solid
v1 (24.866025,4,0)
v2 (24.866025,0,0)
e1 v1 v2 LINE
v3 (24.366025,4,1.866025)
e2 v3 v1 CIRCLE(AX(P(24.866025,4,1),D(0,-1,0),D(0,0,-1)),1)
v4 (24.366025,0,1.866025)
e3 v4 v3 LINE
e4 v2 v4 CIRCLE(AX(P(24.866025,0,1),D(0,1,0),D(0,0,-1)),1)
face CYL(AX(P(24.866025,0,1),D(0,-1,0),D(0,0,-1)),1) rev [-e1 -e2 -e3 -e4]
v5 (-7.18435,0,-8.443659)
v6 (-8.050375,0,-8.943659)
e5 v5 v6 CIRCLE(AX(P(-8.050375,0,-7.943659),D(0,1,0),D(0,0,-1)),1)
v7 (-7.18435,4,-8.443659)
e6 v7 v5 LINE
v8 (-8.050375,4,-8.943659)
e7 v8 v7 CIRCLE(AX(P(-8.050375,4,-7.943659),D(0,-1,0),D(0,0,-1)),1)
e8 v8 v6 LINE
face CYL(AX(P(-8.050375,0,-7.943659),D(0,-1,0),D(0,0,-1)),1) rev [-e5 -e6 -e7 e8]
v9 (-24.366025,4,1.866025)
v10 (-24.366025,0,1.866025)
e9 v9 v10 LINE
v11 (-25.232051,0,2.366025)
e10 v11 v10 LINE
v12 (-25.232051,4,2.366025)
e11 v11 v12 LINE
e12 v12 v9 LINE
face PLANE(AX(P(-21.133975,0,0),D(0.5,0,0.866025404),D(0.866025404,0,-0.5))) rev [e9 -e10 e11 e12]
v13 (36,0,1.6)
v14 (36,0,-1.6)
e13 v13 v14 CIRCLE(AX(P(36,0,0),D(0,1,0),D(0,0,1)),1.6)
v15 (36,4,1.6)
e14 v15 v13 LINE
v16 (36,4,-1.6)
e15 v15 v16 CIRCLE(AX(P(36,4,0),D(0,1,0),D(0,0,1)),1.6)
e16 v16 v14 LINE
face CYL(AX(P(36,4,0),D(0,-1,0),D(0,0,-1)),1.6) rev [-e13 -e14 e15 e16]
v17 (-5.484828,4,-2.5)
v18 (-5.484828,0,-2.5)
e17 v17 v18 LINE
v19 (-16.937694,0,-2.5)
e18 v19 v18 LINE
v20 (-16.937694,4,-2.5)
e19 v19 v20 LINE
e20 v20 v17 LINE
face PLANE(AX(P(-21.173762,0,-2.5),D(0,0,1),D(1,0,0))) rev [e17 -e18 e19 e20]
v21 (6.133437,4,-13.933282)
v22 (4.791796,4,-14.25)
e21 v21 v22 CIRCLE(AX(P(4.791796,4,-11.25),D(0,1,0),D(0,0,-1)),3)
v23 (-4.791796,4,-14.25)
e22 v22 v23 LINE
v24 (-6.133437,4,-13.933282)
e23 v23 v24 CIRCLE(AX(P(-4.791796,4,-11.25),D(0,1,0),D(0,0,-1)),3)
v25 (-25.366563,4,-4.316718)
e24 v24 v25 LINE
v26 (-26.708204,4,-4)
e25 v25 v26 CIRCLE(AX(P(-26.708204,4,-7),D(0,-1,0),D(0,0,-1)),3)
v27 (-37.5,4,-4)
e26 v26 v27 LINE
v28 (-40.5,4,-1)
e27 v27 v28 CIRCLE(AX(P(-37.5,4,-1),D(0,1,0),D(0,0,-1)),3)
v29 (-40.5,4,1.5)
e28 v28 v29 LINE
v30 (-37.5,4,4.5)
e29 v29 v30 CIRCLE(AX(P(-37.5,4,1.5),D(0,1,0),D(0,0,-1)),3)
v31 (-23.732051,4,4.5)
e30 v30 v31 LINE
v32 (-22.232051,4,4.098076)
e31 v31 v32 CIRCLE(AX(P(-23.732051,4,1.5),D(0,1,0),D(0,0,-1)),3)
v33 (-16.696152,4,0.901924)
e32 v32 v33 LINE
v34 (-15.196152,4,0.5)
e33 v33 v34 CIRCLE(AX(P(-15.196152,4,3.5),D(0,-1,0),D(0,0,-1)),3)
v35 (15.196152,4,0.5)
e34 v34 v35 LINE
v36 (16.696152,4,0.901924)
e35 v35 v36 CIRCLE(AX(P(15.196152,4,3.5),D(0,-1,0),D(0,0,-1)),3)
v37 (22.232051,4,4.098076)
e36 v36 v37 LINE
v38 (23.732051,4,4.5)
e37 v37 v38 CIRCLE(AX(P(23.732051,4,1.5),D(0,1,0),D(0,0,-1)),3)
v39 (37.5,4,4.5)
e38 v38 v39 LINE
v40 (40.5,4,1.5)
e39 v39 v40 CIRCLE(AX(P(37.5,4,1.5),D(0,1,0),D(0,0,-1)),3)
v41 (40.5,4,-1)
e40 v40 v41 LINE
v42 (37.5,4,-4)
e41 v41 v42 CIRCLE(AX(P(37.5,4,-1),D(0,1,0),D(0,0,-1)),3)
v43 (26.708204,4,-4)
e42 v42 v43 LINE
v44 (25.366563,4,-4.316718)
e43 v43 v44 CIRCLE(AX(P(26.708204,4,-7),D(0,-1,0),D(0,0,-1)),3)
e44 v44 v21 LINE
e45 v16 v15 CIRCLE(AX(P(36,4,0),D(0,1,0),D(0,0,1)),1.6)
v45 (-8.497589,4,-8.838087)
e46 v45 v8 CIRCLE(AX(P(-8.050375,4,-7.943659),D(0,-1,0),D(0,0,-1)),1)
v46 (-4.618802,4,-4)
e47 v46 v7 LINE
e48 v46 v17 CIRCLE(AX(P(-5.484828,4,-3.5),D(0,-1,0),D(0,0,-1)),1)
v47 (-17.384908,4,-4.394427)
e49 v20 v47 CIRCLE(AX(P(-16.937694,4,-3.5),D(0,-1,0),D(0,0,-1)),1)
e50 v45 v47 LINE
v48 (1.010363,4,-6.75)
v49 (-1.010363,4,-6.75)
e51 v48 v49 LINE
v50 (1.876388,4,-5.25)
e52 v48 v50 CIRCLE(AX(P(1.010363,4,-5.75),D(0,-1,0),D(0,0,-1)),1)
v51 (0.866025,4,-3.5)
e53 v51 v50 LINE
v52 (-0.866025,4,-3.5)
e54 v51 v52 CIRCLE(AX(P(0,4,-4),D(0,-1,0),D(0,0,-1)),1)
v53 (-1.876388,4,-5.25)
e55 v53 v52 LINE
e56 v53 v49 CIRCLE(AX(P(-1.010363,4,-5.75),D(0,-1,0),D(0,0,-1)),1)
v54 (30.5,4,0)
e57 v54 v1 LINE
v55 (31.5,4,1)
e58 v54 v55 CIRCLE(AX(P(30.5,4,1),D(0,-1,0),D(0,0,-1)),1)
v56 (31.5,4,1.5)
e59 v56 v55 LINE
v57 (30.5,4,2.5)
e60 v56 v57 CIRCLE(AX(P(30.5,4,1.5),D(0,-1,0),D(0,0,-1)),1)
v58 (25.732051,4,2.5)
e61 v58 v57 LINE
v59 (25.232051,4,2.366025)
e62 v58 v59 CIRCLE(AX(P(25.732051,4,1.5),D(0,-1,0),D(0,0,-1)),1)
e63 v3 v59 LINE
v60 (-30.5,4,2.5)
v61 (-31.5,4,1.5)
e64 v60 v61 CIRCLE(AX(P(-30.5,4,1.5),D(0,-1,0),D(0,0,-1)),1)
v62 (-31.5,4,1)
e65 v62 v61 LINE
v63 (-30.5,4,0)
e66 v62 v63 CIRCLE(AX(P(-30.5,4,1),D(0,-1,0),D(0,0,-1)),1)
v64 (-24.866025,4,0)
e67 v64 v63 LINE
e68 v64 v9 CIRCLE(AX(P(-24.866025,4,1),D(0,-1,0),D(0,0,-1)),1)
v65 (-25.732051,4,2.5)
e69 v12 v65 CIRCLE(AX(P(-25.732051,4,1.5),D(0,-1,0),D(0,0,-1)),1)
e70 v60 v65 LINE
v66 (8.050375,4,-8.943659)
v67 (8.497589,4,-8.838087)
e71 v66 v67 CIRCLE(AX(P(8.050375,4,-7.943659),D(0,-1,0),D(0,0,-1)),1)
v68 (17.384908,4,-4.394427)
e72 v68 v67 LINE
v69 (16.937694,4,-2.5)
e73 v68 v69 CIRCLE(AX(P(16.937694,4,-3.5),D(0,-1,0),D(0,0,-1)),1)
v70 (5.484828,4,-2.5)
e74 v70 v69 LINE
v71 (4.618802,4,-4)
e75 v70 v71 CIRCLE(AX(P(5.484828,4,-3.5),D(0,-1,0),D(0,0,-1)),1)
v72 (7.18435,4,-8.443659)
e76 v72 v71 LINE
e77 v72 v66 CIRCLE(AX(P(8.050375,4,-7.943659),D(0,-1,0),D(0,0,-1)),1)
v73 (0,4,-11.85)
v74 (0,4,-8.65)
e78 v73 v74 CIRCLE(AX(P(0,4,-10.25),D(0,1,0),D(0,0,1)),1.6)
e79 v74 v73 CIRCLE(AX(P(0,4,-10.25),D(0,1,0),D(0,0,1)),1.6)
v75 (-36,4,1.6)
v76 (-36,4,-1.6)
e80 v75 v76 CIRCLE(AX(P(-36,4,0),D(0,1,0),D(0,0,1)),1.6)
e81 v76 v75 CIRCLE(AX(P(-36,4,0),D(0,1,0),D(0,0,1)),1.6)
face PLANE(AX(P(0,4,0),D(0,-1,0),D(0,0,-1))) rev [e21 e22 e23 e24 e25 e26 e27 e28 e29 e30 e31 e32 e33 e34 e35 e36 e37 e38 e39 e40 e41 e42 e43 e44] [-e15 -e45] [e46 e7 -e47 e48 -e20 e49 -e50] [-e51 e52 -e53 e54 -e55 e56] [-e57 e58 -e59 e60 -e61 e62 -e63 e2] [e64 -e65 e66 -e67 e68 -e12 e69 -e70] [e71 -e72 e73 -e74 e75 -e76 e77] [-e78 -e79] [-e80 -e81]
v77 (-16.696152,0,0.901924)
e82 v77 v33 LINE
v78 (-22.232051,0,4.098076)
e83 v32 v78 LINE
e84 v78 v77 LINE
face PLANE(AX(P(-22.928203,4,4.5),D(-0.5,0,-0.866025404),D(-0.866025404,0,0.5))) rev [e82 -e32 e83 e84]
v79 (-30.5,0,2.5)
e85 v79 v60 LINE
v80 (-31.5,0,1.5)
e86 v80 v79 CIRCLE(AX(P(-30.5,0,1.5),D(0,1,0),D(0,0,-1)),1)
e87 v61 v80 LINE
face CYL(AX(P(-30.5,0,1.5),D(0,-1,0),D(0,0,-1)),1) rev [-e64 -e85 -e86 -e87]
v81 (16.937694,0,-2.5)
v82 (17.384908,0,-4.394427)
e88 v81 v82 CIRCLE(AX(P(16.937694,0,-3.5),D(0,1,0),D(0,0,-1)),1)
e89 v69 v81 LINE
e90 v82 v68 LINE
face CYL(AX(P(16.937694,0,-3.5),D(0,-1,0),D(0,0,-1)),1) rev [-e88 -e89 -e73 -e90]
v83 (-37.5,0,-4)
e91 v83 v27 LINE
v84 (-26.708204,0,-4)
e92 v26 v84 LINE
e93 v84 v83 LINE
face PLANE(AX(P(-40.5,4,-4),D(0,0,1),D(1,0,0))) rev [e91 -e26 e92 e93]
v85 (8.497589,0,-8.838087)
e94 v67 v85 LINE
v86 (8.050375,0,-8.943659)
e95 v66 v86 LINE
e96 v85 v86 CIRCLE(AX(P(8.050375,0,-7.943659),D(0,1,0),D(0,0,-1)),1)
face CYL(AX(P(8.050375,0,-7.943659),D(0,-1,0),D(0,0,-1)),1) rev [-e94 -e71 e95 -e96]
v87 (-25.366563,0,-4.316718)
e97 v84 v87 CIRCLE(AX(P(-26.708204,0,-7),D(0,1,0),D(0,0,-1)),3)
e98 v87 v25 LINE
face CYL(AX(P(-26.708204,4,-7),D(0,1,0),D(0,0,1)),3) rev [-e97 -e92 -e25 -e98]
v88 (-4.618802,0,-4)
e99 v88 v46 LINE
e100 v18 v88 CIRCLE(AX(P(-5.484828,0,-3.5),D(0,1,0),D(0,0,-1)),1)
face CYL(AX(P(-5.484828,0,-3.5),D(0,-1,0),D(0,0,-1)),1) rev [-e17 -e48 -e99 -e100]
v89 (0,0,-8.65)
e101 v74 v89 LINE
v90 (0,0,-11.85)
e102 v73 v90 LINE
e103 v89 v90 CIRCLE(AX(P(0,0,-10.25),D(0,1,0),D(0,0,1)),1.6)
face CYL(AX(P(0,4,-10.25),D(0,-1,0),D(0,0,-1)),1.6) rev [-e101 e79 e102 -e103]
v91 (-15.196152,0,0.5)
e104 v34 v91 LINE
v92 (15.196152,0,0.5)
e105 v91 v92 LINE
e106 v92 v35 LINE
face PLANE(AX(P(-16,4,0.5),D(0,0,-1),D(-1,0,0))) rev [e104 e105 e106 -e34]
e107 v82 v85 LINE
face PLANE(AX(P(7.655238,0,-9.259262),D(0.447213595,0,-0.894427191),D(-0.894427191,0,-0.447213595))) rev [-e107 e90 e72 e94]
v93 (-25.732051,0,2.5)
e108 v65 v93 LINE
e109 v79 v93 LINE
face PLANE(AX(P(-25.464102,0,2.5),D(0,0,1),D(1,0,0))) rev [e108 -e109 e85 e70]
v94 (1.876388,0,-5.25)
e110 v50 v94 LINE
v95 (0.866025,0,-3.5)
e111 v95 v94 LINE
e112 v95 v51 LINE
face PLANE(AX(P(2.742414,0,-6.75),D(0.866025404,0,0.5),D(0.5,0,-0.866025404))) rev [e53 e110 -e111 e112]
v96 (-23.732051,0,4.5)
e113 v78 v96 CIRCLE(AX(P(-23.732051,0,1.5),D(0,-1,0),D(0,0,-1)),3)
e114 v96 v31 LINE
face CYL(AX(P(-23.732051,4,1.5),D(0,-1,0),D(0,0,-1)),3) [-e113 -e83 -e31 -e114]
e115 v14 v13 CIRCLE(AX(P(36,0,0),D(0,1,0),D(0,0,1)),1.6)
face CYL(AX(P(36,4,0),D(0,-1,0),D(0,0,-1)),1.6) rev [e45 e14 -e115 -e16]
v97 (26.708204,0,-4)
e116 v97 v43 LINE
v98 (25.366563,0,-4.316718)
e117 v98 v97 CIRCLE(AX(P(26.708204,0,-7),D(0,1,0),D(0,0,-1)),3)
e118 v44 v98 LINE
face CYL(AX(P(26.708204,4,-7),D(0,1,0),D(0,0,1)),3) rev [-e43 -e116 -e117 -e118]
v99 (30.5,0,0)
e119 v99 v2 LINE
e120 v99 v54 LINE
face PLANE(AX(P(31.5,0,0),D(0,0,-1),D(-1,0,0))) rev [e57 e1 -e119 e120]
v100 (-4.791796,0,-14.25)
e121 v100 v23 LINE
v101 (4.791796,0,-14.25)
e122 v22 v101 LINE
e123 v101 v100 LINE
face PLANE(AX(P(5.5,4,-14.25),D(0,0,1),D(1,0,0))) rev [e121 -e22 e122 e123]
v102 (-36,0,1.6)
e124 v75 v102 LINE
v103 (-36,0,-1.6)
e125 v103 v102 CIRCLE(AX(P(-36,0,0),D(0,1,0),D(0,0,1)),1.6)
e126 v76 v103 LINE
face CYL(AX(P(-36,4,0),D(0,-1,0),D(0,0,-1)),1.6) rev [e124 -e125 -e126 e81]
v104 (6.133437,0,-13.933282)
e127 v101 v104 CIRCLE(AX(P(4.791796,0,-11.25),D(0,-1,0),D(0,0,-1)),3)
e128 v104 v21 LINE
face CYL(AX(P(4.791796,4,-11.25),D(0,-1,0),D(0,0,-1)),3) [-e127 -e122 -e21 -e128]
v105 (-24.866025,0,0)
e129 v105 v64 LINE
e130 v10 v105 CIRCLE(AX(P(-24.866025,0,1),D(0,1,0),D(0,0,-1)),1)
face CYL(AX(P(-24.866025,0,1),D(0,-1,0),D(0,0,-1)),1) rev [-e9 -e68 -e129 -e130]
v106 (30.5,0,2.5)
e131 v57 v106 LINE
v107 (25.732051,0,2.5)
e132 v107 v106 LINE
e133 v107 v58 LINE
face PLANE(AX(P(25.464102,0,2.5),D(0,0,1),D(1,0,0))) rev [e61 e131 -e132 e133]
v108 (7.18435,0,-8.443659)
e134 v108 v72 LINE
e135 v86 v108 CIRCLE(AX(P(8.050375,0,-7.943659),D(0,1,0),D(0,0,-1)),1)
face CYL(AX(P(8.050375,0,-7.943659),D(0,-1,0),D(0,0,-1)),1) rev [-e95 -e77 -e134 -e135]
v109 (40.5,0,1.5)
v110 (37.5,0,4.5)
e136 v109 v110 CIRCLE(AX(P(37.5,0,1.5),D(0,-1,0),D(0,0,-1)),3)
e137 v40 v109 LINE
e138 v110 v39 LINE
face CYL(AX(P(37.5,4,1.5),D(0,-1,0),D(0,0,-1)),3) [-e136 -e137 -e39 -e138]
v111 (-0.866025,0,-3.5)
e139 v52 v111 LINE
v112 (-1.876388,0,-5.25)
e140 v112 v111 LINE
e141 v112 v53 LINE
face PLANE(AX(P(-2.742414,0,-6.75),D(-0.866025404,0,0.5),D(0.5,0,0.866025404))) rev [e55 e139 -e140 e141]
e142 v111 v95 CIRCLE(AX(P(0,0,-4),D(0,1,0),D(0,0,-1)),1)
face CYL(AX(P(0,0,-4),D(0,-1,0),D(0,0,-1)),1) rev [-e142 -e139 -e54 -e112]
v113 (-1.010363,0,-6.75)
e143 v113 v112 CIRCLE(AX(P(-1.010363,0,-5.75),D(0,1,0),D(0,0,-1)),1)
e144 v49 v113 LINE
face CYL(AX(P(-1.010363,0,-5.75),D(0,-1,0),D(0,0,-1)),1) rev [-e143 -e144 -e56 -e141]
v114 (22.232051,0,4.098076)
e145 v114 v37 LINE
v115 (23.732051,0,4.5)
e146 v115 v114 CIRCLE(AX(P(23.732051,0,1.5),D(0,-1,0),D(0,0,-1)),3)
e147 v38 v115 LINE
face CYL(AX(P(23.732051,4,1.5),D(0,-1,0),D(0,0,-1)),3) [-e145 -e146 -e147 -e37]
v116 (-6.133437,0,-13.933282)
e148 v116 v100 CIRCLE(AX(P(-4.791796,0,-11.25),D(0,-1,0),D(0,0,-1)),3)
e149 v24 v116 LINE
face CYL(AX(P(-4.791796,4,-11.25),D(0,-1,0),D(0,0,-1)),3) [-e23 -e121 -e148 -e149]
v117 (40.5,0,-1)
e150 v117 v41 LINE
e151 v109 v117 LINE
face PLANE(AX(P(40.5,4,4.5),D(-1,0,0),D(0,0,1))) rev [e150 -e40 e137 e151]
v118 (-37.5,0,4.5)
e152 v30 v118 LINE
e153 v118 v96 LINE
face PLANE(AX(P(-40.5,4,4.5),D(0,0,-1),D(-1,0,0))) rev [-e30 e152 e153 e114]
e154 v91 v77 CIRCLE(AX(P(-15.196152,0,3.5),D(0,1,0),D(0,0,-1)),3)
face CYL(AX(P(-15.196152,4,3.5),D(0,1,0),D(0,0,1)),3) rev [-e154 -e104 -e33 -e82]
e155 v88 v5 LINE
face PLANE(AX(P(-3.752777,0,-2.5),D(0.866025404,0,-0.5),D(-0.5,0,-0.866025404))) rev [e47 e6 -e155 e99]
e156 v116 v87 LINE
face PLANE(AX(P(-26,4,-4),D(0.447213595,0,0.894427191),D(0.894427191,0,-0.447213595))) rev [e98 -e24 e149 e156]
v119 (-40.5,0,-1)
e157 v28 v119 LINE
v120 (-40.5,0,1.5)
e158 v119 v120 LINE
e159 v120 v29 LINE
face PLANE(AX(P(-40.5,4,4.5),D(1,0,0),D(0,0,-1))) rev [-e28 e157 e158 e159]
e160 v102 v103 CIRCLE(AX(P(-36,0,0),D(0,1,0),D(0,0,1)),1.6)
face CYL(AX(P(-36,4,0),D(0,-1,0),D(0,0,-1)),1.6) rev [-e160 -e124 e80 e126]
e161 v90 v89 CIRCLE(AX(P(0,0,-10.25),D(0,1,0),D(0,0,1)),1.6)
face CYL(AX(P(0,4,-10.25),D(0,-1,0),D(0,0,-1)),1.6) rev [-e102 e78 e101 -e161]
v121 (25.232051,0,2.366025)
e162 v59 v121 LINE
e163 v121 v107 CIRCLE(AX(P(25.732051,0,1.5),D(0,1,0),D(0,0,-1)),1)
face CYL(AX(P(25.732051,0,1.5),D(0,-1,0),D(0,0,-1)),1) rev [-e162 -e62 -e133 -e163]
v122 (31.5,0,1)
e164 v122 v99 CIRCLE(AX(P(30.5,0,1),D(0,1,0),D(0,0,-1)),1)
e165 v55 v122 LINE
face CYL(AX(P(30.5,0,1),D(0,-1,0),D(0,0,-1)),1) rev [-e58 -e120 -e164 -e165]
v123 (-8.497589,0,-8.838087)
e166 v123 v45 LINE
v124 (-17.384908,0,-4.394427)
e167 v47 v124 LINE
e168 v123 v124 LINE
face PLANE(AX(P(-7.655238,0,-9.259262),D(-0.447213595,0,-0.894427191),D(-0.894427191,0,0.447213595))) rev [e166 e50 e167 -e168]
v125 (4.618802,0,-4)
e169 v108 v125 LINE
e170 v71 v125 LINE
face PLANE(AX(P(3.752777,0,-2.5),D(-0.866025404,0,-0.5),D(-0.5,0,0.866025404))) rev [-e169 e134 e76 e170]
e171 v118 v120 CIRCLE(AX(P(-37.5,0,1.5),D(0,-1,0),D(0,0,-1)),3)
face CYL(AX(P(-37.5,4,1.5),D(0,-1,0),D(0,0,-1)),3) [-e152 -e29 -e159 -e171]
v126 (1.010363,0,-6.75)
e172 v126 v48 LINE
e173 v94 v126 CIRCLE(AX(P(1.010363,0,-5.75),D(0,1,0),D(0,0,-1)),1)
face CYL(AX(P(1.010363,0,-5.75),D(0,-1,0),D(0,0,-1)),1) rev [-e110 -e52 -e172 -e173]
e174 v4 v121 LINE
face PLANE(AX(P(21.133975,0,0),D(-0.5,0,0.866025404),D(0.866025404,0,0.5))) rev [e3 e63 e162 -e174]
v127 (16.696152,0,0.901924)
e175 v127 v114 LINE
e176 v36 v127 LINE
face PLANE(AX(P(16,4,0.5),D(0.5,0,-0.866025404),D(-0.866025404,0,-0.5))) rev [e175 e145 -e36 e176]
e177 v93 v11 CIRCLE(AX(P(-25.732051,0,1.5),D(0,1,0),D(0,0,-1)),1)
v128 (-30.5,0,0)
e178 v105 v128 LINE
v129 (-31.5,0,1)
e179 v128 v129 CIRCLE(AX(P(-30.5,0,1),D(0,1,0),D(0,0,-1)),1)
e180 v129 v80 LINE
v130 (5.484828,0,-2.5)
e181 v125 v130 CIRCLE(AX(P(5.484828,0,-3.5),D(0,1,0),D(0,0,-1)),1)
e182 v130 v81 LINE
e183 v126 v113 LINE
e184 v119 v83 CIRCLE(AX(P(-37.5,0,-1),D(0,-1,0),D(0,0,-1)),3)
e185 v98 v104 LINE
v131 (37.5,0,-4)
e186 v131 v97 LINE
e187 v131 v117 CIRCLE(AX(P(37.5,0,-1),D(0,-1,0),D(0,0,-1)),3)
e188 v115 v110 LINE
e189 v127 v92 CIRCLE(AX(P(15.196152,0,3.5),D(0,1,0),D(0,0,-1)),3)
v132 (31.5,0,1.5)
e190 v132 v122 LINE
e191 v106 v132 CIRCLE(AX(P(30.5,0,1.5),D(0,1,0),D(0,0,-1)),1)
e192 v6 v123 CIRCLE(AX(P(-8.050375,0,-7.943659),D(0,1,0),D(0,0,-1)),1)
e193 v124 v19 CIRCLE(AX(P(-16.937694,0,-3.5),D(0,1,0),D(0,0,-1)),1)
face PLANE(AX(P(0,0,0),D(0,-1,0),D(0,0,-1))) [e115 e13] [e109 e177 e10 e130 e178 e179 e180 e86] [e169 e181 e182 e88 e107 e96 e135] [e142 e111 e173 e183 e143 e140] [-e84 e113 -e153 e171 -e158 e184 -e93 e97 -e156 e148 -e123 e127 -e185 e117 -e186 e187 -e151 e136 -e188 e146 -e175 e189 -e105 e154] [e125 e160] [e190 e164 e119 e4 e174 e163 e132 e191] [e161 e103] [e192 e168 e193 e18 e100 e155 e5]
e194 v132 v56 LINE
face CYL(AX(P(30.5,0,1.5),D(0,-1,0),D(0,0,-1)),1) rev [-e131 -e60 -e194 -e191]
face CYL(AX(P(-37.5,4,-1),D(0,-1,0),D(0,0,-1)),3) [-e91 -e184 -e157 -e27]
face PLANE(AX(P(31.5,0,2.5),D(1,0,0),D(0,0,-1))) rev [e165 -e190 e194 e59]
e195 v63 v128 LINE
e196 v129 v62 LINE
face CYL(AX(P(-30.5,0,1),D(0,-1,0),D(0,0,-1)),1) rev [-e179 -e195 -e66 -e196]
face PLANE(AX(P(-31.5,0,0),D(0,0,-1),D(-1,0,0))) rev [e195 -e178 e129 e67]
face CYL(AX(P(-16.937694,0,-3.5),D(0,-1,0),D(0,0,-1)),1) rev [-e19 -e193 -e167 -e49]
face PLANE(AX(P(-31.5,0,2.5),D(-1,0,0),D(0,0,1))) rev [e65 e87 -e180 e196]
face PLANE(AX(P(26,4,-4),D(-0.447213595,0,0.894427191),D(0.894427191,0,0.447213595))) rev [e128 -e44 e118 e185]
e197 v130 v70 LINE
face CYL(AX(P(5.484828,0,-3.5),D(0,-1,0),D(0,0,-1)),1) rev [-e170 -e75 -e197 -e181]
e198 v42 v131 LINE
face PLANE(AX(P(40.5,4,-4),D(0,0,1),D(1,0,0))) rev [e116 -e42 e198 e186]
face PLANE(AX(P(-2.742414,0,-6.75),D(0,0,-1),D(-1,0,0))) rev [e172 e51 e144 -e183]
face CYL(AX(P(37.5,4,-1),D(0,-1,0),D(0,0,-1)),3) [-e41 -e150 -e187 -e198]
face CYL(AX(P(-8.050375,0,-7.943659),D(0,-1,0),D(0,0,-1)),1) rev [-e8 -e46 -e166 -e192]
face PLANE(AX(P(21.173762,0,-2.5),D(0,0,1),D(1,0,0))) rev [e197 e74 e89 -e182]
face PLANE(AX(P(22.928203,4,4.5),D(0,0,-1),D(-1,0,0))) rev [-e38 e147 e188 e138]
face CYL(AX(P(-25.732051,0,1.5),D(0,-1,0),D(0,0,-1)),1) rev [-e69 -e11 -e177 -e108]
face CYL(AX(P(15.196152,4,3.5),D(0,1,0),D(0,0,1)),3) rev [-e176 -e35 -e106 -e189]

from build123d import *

# Parameters (mm, degrees)
SKETCH_1_R          = 1.6
EXTRUDE_1_DEPTH     = 4
CUT_EXTRUDE_1_DEPTH = 44.119746057
FILLET_R1_R         = 1
FILLET_R3_R         = 3


with BuildPart() as part:
    # 草图1 → 凸台-拉伸1 (new body)
    with BuildSketch(Plane(origin=(0, 0, 0), x_dir=(1, 0, 0), z_dir=(0, 1, 0))):
        Polygon((-40.5, -4.5), (-22.92820323, -4.5), (-16, -0.5), (16, -0.5), (22.92820323, -4.5), (40.5, -4.5), (40.5, 4), (26, 4), (5.5, 14.25), (-5.5, 14.25), (-26, 4), (-40.5, 4), align=None)
        with Locations(Location((-36, 0, 0), (0, 0, 270))):
            Circle(SKETCH_1_R, mode=Mode.SUBTRACT)
        with Locations(Location((36, 0, 0), (0, 0, 270))):
            Circle(SKETCH_1_R, mode=Mode.SUBTRACT)
        with Locations(Location((0, 10.25, 0), (0, 0, 270))):
            Circle(SKETCH_1_R, mode=Mode.SUBTRACT)
    extrude(amount=EXTRUDE_1_DEPTH)

    # 草图2 → 切除-拉伸1 (cut, through all)
    with BuildSketch(Plane(origin=(0, 4, 0), x_dir=(1, 0, 0), z_dir=(0, 1, 0))):
        Polygon((-7.655238394, 9.259261842), (-21.173762079, 2.5), (-3.75277675, 2.5), align=None)
        Polygon((-2.742413779, 6.75), (0, 2), (2.742413779, 6.75), align=None)
        Polygon((21.173762079, 2.5), (3.75277675, 2.5), (7.655238394, 9.259261842), align=None)
        Polygon((-31.5, 0), (-21.133974596, 0), (-25.464101615, -2.5), (-31.5, -2.5), align=None)
        Polygon((25.464101615, -2.5), (31.5, -2.5), (31.5, 0), (21.133974596, 0), align=None)
    extrude(amount=-CUT_EXTRUDE_1_DEPTH, mode=Mode.SUBTRACT)

    # R1 镂空圆角
    fillet_r1_edges = [part.edges().sort_by_distance(p)[0] for p in [
        (-25.464101615, 2, 2.5),
        (-31.5, 2, 2.5),
        (-31.5, 2, 0),
        (-21.133974596, 2, 0),
        (25.464101615, 2, 2.5),
        (21.133974596, 2, 0),
        (31.5, 2, 0),
        (31.5, 2, 2.5),
        (7.655238394, 2, -9.259261842),
        (21.173762079, 2, -2.5),
        (3.75277675, 2, -2.5),
        (-2.742413779, 2, -6.75),
        (2.742413779, 2, -6.75),
        (0, 2, -2),
        (-7.655238394, 2, -9.259261842),
        (-3.75277675, 2, -2.5),
        (-21.173762079, 2, -2.5),
    ]]
    fillet(fillet_r1_edges, radius=FILLET_R1_R)

    # R3 外缘圆角
    fillet_r3_edges = [part.edges().sort_by_distance(p)[0] for p in [
        (40.5, 2, -4),
        (40.5, 2, 4.5),
        (22.92820323, 2, 4.5),
        (16, 2, 0.5),
        (-16, 2, 0.5),
        (-22.92820323, 2, 4.5),
        (-40.5, 2, 4.5),
        (-40.5, 2, -4),
        (-26, 2, -4),
        (-5.5, 2, -14.25),
        (5.5, 2, -14.25),
        (26, 2, -4),
    ]]
    fillet(fillet_r3_edges, radius=FILLET_R3_R)


solid = part.part
